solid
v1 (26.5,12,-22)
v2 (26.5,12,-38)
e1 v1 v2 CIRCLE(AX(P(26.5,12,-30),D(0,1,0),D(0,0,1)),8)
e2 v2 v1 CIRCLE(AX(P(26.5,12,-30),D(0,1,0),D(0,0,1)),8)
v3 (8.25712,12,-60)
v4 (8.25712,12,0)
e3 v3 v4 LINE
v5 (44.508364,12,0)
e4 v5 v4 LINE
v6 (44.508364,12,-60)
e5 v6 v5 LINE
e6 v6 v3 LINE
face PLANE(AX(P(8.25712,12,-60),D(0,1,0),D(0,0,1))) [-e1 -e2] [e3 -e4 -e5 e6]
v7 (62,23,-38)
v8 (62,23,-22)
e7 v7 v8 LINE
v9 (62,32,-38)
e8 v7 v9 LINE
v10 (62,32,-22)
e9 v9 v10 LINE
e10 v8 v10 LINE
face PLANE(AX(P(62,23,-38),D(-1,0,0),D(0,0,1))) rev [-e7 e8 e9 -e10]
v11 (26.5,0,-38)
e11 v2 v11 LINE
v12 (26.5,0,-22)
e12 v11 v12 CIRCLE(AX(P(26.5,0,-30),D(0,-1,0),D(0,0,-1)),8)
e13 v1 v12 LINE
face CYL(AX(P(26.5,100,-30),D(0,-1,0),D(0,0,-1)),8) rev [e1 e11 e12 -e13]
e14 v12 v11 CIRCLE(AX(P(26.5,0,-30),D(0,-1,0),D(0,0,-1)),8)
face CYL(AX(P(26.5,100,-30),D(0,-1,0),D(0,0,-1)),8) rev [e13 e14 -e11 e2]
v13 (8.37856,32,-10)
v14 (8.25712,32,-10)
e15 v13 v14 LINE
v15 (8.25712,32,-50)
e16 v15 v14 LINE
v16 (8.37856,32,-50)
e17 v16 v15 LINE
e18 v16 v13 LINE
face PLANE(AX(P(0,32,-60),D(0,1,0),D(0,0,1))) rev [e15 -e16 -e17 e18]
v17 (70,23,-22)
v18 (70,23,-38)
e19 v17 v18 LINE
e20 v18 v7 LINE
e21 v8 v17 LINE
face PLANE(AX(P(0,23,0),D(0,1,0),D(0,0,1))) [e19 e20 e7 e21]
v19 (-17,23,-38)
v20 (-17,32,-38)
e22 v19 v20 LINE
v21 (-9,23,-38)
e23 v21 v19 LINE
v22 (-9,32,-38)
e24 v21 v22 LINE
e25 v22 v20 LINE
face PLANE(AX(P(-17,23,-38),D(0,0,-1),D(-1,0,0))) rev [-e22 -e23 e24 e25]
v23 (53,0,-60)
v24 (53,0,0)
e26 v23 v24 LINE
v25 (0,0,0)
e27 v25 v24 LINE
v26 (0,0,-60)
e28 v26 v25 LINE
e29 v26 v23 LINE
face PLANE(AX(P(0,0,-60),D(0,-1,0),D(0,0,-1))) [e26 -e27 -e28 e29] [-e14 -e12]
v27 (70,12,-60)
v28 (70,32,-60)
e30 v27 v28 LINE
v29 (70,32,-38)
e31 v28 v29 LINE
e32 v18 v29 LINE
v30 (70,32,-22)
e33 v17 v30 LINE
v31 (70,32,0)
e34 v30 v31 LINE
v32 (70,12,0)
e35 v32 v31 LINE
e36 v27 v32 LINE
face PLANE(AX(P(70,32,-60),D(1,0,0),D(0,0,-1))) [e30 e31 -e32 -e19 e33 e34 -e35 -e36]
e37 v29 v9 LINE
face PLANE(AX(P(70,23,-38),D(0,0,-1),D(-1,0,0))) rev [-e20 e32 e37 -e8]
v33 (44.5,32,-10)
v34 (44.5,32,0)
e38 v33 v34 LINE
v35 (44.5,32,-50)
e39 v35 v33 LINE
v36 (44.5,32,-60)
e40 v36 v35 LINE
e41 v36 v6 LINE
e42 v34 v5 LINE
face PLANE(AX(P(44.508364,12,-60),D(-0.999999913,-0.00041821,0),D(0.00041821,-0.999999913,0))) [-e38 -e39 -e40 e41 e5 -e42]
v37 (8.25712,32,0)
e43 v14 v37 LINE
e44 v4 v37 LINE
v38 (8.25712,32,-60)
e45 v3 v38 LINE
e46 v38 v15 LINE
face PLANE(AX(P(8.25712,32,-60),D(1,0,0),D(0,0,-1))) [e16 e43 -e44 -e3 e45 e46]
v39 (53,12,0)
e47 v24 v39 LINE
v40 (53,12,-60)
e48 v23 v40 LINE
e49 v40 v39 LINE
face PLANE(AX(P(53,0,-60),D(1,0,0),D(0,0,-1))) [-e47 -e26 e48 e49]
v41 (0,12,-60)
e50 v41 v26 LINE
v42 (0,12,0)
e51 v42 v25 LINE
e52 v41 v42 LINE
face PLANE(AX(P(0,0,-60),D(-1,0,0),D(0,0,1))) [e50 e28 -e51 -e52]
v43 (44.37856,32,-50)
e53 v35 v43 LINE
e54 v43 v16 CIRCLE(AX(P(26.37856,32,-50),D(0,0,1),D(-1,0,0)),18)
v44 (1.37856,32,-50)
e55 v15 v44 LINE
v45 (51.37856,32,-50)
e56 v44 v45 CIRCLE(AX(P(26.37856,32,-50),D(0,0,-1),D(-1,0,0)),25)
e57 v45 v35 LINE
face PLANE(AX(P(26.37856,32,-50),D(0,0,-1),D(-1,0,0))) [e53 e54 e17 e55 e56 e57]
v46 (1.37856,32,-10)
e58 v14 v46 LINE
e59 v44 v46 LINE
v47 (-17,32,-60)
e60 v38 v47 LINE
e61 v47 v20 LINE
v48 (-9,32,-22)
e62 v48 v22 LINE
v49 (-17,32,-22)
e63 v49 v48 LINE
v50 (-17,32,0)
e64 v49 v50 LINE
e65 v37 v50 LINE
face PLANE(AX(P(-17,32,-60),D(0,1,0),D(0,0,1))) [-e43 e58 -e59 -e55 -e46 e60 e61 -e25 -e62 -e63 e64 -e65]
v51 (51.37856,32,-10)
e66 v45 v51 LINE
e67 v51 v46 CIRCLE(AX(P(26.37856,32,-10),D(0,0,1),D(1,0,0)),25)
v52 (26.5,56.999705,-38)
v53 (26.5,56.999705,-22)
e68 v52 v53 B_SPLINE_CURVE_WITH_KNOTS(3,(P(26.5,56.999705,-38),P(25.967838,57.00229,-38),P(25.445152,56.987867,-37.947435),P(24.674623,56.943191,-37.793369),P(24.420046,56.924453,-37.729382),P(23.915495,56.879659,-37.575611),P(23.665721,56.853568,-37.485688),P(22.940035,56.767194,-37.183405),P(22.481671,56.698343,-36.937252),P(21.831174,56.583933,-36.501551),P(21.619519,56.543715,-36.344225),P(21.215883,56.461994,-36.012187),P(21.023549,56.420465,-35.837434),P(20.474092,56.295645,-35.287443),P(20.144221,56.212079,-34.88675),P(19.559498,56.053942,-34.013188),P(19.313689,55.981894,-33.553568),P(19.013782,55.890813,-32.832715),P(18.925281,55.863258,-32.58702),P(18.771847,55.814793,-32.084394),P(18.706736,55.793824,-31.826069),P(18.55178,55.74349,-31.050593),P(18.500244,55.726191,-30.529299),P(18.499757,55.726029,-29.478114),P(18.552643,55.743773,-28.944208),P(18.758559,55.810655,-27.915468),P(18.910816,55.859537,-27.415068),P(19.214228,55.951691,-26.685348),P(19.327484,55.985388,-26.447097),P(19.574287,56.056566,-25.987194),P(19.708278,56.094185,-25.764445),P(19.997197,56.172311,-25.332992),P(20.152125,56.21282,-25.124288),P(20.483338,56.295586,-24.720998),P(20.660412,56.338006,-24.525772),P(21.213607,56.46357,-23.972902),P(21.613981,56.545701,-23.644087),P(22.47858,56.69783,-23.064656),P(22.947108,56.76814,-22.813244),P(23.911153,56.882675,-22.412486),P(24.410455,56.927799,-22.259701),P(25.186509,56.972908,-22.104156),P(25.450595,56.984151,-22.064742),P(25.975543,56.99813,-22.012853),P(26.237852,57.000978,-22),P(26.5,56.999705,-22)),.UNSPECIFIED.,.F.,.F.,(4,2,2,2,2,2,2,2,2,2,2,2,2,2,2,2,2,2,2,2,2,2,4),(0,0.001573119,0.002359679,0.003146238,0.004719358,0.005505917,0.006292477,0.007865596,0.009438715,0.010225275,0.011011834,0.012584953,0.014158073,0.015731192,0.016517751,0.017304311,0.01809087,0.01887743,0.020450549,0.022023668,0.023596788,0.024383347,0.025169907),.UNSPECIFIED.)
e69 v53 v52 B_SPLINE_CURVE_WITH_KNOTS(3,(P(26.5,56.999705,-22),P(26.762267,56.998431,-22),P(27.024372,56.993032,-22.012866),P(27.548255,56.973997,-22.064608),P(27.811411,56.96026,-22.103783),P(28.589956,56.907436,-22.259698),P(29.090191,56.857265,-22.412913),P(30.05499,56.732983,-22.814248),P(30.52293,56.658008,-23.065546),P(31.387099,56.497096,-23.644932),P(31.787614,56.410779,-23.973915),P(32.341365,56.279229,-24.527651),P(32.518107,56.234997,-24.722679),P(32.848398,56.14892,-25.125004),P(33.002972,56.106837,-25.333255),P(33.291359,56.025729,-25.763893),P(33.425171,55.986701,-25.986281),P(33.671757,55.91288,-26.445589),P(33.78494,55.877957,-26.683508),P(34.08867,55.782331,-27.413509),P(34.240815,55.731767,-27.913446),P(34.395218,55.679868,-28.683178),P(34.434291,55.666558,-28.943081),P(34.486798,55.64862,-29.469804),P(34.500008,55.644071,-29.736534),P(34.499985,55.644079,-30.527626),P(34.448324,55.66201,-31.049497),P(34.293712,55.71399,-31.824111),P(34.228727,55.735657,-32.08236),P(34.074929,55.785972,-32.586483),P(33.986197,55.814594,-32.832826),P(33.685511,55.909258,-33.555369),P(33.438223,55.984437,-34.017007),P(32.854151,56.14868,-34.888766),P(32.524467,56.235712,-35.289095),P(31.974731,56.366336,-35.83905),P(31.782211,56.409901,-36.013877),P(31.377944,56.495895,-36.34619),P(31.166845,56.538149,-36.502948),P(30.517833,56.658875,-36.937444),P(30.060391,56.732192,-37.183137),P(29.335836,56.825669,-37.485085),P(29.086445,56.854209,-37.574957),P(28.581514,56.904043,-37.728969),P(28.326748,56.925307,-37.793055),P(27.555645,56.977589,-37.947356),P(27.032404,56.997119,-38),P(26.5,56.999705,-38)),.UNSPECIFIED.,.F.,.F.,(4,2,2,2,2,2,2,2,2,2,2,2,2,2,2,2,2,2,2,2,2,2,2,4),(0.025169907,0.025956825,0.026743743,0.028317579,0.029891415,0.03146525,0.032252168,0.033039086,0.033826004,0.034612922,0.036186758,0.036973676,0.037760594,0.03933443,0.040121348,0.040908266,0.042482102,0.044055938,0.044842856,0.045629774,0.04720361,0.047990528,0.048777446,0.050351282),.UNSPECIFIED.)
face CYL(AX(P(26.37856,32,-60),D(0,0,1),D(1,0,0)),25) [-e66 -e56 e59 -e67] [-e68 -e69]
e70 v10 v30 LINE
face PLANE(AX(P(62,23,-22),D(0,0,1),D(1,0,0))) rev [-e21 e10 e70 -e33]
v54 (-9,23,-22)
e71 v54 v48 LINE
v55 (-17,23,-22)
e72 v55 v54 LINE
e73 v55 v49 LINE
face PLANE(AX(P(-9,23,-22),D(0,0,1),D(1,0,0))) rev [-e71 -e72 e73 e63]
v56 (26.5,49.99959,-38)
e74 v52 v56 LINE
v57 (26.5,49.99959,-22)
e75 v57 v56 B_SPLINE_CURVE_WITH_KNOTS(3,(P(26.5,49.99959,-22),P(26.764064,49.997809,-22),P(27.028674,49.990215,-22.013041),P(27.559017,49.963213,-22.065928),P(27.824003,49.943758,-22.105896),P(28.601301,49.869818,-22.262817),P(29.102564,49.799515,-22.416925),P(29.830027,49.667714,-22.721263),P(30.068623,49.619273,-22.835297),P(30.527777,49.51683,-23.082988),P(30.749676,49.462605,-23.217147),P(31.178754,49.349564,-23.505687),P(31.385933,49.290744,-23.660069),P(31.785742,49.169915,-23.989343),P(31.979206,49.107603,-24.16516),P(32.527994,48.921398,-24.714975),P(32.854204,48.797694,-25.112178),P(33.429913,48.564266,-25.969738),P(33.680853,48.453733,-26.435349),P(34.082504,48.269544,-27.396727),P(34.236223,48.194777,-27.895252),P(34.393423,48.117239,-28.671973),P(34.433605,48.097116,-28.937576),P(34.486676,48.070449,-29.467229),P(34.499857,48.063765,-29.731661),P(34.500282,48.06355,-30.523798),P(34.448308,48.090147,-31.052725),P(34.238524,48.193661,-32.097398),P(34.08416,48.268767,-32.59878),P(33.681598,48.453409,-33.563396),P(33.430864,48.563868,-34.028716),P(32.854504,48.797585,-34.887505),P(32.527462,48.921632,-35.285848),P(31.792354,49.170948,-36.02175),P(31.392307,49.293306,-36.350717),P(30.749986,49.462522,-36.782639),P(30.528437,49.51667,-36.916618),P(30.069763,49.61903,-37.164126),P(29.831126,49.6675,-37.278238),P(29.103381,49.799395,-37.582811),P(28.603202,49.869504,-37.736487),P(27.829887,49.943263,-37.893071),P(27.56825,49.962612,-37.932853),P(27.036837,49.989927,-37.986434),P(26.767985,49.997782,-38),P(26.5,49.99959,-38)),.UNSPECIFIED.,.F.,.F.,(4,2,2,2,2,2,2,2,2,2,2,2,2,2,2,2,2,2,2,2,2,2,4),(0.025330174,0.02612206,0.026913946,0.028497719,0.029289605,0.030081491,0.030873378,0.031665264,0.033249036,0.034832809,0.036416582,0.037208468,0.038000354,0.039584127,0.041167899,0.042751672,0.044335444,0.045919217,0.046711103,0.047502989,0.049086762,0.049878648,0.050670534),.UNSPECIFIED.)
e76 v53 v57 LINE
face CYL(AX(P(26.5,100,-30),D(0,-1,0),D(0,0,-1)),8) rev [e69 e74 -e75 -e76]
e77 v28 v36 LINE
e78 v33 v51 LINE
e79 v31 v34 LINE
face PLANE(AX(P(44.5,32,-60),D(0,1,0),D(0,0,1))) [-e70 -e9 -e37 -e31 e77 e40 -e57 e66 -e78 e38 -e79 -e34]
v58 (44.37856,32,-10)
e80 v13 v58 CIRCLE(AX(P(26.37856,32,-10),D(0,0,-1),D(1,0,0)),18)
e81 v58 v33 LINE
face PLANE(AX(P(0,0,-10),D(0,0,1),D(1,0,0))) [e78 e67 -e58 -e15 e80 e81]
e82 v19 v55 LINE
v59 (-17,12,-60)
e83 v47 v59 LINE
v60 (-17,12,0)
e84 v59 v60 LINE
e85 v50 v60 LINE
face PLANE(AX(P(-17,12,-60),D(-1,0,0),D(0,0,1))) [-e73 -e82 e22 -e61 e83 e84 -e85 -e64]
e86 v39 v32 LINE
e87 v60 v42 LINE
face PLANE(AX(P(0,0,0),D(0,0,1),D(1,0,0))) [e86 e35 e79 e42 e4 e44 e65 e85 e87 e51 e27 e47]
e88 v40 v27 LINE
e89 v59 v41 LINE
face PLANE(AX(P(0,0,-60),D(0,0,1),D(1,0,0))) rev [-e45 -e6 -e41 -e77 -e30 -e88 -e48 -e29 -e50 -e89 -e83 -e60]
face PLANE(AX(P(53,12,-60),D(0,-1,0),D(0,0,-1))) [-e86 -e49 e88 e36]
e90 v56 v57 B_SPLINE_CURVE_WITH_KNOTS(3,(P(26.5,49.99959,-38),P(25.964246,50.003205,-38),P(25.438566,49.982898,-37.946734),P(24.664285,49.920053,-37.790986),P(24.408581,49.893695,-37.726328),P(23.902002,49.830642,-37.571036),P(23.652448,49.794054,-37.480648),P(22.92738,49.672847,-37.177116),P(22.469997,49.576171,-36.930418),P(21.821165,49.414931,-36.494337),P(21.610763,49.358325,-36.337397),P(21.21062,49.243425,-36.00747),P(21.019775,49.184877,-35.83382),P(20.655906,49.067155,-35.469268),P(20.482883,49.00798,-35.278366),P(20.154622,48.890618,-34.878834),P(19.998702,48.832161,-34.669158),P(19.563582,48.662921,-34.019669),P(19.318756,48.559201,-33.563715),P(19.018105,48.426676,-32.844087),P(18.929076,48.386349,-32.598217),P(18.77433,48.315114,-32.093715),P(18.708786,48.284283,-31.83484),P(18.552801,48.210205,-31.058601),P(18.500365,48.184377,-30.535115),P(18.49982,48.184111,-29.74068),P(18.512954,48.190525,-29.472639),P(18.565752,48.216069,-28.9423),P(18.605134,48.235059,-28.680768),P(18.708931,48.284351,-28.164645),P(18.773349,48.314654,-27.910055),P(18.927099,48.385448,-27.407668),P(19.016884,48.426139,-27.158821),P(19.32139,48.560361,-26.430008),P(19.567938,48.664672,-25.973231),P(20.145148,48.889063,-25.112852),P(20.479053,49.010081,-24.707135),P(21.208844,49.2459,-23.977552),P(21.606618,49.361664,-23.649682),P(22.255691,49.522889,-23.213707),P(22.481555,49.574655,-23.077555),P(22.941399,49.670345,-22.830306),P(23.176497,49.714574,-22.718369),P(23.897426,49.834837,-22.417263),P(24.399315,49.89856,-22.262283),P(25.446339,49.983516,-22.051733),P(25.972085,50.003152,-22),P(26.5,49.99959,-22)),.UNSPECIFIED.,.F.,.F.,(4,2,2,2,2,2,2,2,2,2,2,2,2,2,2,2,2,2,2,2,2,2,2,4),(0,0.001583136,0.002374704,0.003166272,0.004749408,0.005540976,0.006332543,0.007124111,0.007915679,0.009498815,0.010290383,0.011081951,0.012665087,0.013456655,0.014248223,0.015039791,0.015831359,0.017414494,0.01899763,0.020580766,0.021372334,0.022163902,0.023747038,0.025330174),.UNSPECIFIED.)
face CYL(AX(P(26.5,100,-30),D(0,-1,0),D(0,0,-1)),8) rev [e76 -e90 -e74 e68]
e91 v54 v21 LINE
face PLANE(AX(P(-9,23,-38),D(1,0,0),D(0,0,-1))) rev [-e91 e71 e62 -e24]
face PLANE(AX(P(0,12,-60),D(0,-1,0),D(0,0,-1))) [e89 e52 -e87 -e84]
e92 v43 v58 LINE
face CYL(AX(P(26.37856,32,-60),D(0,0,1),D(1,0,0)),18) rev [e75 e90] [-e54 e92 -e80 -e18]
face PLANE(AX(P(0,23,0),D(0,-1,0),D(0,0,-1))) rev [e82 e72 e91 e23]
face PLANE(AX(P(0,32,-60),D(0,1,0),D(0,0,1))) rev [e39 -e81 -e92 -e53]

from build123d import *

# Parameters (mm, degrees)
BASE_BLOCK_DEPTH             = 60
SADDLE_ARCH_DEPTH            = 60
BEARING_SEAT_CUT_FRONT_DEPTH = 10
BEARING_START                = -10
BEARING_SEAT_CUT_REAR_DEPTH  = 10
OIL_HOLE_SKETCH_R            = 8
OIL_HOLE_8_DEPTH             = 100
LOCATING_SLOTS_SKETCH_W      = 8
LOCATING_SLOTS_SKETCH_H      = 16
LOCATING_SLOTS_DEPTH         = 9


with BuildPart() as part:
    # Base Block Profile → Base Block (new body)
    with BuildSketch(Plane.XY):
        Polygon((0, 0), (53, 0), (53, 12), (70, 12), (70, 32), (44.5, 32), (44.508364197, 12), (8.257120322, 12), (8.257120322, 32), (-17, 32), (-17, 12), (0, 12), align=None)
    extrude(amount=-BASE_BLOCK_DEPTH)

    # Saddle Arch Profile → Saddle Arch (add)
    with BuildSketch(Plane.XY):
        with BuildLine():
            Line((1.378560161, 32), (8.257120322, 32))
            Line((8.257120322, 32), (8.378560161, 32))
            ThreePointArc((8.378560161, 32), (26.378560161, 50), (44.378560161, 32))
            Line((44.378560161, 32), (44.5, 32))
            Line((44.5, 32), (51.378560161, 32))
            ThreePointArc((51.378560161, 32), (26.378560161, 57), (1.378560161, 32))
        make_face()
    extrude(amount=-SADDLE_ARCH_DEPTH)

    # Bearing Seat Front Profile → Bearing Seat Cut Front (cut)
    with BuildSketch(Plane.XY):
        with BuildLine():
            Line((1.378560161, 32), (8.257120322, 32))
            Line((8.257120322, 32), (8.378560161, 32))
            ThreePointArc((8.378560161, 32), (26.378560161, 50), (44.378560161, 32))
            Line((44.378560161, 32), (44.5, 32))
            Line((44.5, 32), (51.378560161, 32))
            ThreePointArc((51.378560161, 32), (26.378560161, 57), (1.378560161, 32))
        make_face()
    extrude(amount=-BEARING_SEAT_CUT_FRONT_DEPTH, mode=Mode.SUBTRACT)

    # Bearing Seat Rear Profile → Bearing Seat Cut Rear (cut)
    with BuildSketch(Plane(origin=(0, 0, -60), x_dir=(-1, 0, 0), z_dir=(0, 0, -1)).offset(BEARING_START)):
        with BuildLine():
            Line((-51.378560161, 32), (-44.378560161, 32))
            ThreePointArc((-44.378560161, 32), (-26.378560161, 50), (-8.378560161, 32))
            Line((-8.378560161, 32), (-1.378560161, 32))
            ThreePointArc((-1.378560161, 32), (-26.378560161, 57), (-51.378560161, 32))
        make_face()
    extrude(amount=BEARING_SEAT_CUT_REAR_DEPTH, mode=Mode.SUBTRACT)

    # Oil Hole Sketch → Oil Hole Ø8 (cut)
    with BuildSketch(Plane.XZ):
        with Locations(Location((26.5, -30, 0), (0, 0, 270))):
            Circle(OIL_HOLE_SKETCH_R)
    extrude(amount=-OIL_HOLE_8_DEPTH, mode=Mode.SUBTRACT)

    # Locating Slots Sketch → Locating Slots (cut)
    with BuildSketch(Plane(origin=(0, 32, 0), x_dir=(1, 0, 0), z_dir=(0, 1, 0))):
        with Locations((-13, 30)):
            Rectangle(LOCATING_SLOTS_SKETCH_W, LOCATING_SLOTS_SKETCH_H)
        Polygon((70, 30), (70, 38), (62, 38), (62, 22), (70, 22), align=None)
    extrude(amount=-LOCATING_SLOTS_DEPTH, mode=Mode.SUBTRACT)


solid = part.part
